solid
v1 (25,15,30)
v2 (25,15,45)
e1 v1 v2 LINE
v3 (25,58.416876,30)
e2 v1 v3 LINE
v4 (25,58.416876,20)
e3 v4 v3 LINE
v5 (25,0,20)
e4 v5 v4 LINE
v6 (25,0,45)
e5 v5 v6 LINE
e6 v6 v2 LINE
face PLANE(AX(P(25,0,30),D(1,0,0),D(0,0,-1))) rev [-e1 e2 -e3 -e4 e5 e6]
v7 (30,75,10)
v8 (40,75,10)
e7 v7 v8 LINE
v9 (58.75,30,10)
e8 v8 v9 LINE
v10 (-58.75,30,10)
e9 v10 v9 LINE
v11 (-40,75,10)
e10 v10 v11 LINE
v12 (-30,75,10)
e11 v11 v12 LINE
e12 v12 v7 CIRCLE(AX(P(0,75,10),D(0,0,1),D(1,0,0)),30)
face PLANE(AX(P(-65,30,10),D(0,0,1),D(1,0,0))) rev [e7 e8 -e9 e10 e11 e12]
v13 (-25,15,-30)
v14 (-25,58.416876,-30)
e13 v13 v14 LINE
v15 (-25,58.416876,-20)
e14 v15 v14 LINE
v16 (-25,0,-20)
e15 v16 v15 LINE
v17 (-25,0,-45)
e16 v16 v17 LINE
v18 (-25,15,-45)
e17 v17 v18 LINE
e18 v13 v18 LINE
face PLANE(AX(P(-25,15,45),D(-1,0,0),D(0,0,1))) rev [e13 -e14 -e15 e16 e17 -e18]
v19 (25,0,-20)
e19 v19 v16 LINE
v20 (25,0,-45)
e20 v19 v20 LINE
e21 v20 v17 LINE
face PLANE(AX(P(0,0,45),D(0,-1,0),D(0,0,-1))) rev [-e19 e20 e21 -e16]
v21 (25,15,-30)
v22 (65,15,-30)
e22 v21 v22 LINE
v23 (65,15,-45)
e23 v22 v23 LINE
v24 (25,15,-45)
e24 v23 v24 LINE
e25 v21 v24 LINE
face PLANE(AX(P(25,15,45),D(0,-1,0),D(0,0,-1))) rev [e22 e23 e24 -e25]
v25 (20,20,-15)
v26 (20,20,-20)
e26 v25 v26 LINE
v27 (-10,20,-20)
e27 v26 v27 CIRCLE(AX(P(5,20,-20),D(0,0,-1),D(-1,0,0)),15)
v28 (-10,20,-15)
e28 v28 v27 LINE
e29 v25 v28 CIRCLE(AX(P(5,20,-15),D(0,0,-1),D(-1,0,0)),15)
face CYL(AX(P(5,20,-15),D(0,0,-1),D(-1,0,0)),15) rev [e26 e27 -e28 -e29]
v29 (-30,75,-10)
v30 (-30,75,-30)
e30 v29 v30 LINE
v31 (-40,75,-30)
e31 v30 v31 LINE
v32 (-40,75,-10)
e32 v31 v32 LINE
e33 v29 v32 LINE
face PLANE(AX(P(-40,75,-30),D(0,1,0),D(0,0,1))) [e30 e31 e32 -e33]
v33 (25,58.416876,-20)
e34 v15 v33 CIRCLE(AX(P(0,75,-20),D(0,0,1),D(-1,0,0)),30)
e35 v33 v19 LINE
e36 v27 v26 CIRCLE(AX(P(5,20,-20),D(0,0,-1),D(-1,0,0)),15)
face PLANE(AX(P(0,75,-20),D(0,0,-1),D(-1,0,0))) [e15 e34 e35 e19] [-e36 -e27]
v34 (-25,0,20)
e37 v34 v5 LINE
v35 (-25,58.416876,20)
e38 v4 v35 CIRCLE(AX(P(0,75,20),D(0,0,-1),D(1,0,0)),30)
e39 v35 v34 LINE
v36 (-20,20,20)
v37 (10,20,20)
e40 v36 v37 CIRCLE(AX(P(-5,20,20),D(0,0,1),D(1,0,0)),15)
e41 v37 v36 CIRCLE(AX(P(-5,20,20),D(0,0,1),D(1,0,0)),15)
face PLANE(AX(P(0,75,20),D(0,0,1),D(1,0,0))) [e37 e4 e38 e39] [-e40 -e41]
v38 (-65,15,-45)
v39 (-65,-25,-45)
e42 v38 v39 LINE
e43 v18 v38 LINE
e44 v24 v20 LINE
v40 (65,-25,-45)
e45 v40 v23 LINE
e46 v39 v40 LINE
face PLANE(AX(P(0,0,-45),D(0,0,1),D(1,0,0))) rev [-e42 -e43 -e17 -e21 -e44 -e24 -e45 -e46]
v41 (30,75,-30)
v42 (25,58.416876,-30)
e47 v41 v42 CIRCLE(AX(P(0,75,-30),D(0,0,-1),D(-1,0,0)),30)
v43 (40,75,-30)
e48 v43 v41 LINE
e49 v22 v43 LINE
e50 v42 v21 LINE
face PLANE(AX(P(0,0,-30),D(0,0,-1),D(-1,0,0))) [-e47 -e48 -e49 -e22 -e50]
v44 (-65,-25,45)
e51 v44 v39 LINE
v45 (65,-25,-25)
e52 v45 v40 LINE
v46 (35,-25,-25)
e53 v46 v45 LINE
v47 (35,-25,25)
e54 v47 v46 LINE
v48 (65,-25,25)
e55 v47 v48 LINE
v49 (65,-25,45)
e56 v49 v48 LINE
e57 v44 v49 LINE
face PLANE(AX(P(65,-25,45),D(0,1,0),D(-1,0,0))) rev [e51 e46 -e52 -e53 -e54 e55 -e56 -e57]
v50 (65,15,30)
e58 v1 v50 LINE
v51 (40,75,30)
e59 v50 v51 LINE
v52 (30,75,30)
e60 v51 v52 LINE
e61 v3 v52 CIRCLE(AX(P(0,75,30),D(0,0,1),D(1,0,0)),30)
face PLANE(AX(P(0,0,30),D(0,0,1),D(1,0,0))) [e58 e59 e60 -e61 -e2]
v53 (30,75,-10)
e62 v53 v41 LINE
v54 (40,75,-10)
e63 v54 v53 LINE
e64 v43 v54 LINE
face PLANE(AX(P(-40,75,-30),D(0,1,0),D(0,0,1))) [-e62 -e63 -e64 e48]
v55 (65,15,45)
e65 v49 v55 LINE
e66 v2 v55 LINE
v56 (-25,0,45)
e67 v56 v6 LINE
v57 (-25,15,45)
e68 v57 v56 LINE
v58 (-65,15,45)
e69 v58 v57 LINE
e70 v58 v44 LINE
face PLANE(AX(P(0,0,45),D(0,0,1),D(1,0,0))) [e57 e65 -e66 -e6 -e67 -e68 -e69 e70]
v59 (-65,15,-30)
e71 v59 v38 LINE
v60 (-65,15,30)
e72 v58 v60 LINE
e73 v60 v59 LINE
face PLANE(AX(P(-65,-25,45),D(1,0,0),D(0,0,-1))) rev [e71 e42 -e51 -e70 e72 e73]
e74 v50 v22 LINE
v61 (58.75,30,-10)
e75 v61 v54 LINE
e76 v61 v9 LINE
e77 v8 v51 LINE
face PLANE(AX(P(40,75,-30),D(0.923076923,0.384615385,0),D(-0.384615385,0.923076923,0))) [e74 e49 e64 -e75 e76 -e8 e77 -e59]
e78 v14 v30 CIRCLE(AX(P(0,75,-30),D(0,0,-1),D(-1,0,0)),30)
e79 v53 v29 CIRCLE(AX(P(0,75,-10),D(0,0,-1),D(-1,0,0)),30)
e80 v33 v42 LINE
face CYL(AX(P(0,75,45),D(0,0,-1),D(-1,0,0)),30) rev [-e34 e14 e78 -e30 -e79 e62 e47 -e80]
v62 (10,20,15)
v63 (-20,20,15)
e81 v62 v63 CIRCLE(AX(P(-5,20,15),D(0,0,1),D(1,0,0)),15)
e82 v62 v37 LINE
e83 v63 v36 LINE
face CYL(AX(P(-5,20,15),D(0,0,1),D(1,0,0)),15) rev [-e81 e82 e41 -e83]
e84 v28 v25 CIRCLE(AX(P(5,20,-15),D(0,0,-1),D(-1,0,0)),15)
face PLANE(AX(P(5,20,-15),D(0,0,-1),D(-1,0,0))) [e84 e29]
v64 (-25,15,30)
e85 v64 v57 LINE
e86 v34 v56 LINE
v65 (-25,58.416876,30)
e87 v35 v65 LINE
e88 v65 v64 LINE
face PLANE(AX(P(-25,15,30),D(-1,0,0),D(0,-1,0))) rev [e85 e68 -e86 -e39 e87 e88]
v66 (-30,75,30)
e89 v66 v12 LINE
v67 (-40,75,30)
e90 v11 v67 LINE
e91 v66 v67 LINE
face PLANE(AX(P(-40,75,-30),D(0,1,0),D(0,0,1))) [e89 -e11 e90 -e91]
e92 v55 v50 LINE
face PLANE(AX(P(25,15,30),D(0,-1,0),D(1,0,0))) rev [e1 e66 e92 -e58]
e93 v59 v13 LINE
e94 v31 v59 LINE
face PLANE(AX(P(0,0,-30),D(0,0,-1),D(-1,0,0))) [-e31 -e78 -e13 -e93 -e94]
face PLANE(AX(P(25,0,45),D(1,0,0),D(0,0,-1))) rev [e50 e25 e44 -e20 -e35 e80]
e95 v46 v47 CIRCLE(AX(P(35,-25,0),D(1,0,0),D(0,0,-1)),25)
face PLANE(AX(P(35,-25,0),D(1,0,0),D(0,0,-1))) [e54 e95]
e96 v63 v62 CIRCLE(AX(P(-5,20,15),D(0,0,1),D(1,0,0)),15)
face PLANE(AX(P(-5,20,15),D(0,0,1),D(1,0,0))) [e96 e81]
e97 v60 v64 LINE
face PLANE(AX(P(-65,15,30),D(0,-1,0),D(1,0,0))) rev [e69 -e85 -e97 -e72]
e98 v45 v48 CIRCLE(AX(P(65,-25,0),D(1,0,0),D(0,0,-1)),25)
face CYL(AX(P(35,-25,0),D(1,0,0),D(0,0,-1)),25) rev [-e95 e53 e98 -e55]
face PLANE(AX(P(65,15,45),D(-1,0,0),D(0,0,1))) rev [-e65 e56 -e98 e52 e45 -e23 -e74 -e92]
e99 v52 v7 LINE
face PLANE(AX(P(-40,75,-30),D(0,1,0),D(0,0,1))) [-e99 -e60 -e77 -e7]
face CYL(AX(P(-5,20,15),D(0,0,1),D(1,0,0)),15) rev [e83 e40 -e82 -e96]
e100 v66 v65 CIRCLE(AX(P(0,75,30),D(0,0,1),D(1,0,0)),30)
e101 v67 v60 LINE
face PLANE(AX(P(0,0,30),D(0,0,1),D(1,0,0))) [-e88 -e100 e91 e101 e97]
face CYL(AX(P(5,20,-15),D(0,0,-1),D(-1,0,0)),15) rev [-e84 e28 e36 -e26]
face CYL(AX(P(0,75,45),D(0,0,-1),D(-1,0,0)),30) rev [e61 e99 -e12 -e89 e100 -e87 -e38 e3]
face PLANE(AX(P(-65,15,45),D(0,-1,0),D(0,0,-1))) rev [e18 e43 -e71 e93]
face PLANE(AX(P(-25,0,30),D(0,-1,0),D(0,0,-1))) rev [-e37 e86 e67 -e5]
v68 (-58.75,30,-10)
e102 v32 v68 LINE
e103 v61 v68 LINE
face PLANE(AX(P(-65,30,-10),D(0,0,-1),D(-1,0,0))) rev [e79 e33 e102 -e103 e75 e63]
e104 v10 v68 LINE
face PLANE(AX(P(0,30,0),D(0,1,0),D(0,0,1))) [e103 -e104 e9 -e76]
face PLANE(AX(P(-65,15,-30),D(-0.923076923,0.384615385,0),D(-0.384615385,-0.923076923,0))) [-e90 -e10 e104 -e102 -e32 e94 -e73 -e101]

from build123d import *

# Parameters (mm, degrees)
BASE_BLOCK_DEPTH        = 45
BOTTOM_ARCH_CUT_DEPTH   = 30
BEARING_PEDESTAL_DEPTH  = 75
PEDESTAL_SIDE_CUT_DEPTH = 15
BEARING_SEAT_PROFILE_W  = 130
BEARING_SEAT_PROFILE_H  = 20
BEARING_SEAT_CUT_DEPTH  = 45
CROSS_HOLE_DEPTH        = 114.468057179
CROSS_HOLE_DEPTH_BACK   = 114.468057179
SLOT_A_CUT_DEPTH        = 10
SLOT_START              = -10
SLOT_B_CUT_DEPTH        = 10
STEP_RECESS_A_PROFILE_R = 15
STEP_RECESS_A_DEPTH     = 5
STEP_RECESS_B_PROFILE_R = 15
STEP_RECESS_B_DEPTH     = 5


with BuildPart() as part:
    # Base Block Profile → Base Block (new, symmetric)
    with BuildSketch(Plane.XY):
        Polygon((0, 0), (25, 0), (25, 15), (65, 15), (65, -25), (-65, -25), (-65, 15), (-25, 15), (-25, 0), align=None)
    extrude(amount=BASE_BLOCK_DEPTH, both=True)

    # Bottom Arch Profile R25 → Bottom Arch Cut (cut)
    with BuildSketch(Plane(origin=(65, 0, 0), x_dir=(0, 0, -1), z_dir=(1, 0, 0))):
        with BuildLine():
            Line((-25, -25), (25, -25))
            ThreePointArc((25, -25), (0, 0), (-25, -25))
        make_face()
    extrude(amount=-BOTTOM_ARCH_CUT_DEPTH, mode=Mode.SUBTRACT)

    # Pedestal Profile → Bearing Pedestal (add)
    with BuildSketch(Plane.XY.offset(45)):
        Polygon((-65, 15), (-40, 75), (40, 75), (65, 15), (25, 15), (25, 0), (-25, 0), (-25, 15), align=None)
    extrude(amount=-BEARING_PEDESTAL_DEPTH)

    # Pedestal Side Cut Profile → Pedestal Side Cut (cut)
    with BuildSketch(Plane.XY.offset(45)):
        Polygon((-65, 15), (-25, 15), (-25, 0), (25, 0), (25, 15), (65, 15), (40, 75), (-40, 75), align=None)
    extrude(amount=-PEDESTAL_SIDE_CUT_DEPTH, mode=Mode.SUBTRACT)

    # Bearing Seat Profile → Bearing Seat Cut (cut)
    with BuildSketch(Plane(origin=(0, 75, 0), x_dir=(1, 0, 0), z_dir=(0, 1, 0))):
        Rectangle(BEARING_SEAT_PROFILE_W, BEARING_SEAT_PROFILE_H)
    extrude(amount=-BEARING_SEAT_CUT_DEPTH, mode=Mode.SUBTRACT)

    # Cross Hole Profile → Cross Hole (cut, two sides: drawn at the far end of the back side and taken through both)
    with BuildSketch(Plane(origin=(0, 0, 10), x_dir=(-1, 0, 0), z_dir=(0, 0, -1)).offset(-CROSS_HOLE_DEPTH_BACK)):
        with BuildLine():
            Line((-30, 75), (30, 75))
            ThreePointArc((30, 75), (0, 45), (-30, 75))
        make_face()
    extrude(amount=CROSS_HOLE_DEPTH + CROSS_HOLE_DEPTH_BACK, mode=Mode.SUBTRACT)

    # Slot A Profile → Slot A Cut (cut)
    with BuildSketch(Plane.XY.offset(30)):
        with BuildLine():
            Line((-25, 0), (-25, 58.416876048))
            ThreePointArc((-25, 58.416876048), (0, 45), (25, 58.416876048))
            Line((25, 58.416876048), (25, 0))
            Line((25, 0), (-25, 0))
        make_face()
    extrude(amount=-SLOT_A_CUT_DEPTH, mode=Mode.SUBTRACT)

    # Slot B Profile → Slot B Cut (cut)
    with BuildSketch(Plane(origin=(0, 0, -30), x_dir=(-1, 0, 0), z_dir=(0, 0, -1)).offset(SLOT_START)):
        with BuildLine():
            Line((-25, 0), (25, 0))
            Line((25, 0), (25, 58.416876048))
            ThreePointArc((25, 58.416876048), (0, 45), (-25, 58.416876048))
            Line((-25, 58.416876048), (-25, 0))
        make_face()
    extrude(amount=SLOT_B_CUT_DEPTH, mode=Mode.SUBTRACT)

    # Step Recess A Profile → Step Recess A (cut)
    with BuildSketch(Plane(origin=(0, 0, -20), x_dir=(-1, 0, 0), z_dir=(0, 0, -1))):
        with Locations((-5, 20)):
            Circle(STEP_RECESS_A_PROFILE_R)
    extrude(amount=-STEP_RECESS_A_DEPTH, mode=Mode.SUBTRACT)

    # Step Recess B Profile → Step Recess B (cut)
    with BuildSketch(Plane.XY.offset(20)):
        with Locations((-5, 20)):
            Circle(STEP_RECESS_B_PROFILE_R)
    extrude(amount=-STEP_RECESS_B_DEPTH, mode=Mode.SUBTRACT)


solid = part.part
